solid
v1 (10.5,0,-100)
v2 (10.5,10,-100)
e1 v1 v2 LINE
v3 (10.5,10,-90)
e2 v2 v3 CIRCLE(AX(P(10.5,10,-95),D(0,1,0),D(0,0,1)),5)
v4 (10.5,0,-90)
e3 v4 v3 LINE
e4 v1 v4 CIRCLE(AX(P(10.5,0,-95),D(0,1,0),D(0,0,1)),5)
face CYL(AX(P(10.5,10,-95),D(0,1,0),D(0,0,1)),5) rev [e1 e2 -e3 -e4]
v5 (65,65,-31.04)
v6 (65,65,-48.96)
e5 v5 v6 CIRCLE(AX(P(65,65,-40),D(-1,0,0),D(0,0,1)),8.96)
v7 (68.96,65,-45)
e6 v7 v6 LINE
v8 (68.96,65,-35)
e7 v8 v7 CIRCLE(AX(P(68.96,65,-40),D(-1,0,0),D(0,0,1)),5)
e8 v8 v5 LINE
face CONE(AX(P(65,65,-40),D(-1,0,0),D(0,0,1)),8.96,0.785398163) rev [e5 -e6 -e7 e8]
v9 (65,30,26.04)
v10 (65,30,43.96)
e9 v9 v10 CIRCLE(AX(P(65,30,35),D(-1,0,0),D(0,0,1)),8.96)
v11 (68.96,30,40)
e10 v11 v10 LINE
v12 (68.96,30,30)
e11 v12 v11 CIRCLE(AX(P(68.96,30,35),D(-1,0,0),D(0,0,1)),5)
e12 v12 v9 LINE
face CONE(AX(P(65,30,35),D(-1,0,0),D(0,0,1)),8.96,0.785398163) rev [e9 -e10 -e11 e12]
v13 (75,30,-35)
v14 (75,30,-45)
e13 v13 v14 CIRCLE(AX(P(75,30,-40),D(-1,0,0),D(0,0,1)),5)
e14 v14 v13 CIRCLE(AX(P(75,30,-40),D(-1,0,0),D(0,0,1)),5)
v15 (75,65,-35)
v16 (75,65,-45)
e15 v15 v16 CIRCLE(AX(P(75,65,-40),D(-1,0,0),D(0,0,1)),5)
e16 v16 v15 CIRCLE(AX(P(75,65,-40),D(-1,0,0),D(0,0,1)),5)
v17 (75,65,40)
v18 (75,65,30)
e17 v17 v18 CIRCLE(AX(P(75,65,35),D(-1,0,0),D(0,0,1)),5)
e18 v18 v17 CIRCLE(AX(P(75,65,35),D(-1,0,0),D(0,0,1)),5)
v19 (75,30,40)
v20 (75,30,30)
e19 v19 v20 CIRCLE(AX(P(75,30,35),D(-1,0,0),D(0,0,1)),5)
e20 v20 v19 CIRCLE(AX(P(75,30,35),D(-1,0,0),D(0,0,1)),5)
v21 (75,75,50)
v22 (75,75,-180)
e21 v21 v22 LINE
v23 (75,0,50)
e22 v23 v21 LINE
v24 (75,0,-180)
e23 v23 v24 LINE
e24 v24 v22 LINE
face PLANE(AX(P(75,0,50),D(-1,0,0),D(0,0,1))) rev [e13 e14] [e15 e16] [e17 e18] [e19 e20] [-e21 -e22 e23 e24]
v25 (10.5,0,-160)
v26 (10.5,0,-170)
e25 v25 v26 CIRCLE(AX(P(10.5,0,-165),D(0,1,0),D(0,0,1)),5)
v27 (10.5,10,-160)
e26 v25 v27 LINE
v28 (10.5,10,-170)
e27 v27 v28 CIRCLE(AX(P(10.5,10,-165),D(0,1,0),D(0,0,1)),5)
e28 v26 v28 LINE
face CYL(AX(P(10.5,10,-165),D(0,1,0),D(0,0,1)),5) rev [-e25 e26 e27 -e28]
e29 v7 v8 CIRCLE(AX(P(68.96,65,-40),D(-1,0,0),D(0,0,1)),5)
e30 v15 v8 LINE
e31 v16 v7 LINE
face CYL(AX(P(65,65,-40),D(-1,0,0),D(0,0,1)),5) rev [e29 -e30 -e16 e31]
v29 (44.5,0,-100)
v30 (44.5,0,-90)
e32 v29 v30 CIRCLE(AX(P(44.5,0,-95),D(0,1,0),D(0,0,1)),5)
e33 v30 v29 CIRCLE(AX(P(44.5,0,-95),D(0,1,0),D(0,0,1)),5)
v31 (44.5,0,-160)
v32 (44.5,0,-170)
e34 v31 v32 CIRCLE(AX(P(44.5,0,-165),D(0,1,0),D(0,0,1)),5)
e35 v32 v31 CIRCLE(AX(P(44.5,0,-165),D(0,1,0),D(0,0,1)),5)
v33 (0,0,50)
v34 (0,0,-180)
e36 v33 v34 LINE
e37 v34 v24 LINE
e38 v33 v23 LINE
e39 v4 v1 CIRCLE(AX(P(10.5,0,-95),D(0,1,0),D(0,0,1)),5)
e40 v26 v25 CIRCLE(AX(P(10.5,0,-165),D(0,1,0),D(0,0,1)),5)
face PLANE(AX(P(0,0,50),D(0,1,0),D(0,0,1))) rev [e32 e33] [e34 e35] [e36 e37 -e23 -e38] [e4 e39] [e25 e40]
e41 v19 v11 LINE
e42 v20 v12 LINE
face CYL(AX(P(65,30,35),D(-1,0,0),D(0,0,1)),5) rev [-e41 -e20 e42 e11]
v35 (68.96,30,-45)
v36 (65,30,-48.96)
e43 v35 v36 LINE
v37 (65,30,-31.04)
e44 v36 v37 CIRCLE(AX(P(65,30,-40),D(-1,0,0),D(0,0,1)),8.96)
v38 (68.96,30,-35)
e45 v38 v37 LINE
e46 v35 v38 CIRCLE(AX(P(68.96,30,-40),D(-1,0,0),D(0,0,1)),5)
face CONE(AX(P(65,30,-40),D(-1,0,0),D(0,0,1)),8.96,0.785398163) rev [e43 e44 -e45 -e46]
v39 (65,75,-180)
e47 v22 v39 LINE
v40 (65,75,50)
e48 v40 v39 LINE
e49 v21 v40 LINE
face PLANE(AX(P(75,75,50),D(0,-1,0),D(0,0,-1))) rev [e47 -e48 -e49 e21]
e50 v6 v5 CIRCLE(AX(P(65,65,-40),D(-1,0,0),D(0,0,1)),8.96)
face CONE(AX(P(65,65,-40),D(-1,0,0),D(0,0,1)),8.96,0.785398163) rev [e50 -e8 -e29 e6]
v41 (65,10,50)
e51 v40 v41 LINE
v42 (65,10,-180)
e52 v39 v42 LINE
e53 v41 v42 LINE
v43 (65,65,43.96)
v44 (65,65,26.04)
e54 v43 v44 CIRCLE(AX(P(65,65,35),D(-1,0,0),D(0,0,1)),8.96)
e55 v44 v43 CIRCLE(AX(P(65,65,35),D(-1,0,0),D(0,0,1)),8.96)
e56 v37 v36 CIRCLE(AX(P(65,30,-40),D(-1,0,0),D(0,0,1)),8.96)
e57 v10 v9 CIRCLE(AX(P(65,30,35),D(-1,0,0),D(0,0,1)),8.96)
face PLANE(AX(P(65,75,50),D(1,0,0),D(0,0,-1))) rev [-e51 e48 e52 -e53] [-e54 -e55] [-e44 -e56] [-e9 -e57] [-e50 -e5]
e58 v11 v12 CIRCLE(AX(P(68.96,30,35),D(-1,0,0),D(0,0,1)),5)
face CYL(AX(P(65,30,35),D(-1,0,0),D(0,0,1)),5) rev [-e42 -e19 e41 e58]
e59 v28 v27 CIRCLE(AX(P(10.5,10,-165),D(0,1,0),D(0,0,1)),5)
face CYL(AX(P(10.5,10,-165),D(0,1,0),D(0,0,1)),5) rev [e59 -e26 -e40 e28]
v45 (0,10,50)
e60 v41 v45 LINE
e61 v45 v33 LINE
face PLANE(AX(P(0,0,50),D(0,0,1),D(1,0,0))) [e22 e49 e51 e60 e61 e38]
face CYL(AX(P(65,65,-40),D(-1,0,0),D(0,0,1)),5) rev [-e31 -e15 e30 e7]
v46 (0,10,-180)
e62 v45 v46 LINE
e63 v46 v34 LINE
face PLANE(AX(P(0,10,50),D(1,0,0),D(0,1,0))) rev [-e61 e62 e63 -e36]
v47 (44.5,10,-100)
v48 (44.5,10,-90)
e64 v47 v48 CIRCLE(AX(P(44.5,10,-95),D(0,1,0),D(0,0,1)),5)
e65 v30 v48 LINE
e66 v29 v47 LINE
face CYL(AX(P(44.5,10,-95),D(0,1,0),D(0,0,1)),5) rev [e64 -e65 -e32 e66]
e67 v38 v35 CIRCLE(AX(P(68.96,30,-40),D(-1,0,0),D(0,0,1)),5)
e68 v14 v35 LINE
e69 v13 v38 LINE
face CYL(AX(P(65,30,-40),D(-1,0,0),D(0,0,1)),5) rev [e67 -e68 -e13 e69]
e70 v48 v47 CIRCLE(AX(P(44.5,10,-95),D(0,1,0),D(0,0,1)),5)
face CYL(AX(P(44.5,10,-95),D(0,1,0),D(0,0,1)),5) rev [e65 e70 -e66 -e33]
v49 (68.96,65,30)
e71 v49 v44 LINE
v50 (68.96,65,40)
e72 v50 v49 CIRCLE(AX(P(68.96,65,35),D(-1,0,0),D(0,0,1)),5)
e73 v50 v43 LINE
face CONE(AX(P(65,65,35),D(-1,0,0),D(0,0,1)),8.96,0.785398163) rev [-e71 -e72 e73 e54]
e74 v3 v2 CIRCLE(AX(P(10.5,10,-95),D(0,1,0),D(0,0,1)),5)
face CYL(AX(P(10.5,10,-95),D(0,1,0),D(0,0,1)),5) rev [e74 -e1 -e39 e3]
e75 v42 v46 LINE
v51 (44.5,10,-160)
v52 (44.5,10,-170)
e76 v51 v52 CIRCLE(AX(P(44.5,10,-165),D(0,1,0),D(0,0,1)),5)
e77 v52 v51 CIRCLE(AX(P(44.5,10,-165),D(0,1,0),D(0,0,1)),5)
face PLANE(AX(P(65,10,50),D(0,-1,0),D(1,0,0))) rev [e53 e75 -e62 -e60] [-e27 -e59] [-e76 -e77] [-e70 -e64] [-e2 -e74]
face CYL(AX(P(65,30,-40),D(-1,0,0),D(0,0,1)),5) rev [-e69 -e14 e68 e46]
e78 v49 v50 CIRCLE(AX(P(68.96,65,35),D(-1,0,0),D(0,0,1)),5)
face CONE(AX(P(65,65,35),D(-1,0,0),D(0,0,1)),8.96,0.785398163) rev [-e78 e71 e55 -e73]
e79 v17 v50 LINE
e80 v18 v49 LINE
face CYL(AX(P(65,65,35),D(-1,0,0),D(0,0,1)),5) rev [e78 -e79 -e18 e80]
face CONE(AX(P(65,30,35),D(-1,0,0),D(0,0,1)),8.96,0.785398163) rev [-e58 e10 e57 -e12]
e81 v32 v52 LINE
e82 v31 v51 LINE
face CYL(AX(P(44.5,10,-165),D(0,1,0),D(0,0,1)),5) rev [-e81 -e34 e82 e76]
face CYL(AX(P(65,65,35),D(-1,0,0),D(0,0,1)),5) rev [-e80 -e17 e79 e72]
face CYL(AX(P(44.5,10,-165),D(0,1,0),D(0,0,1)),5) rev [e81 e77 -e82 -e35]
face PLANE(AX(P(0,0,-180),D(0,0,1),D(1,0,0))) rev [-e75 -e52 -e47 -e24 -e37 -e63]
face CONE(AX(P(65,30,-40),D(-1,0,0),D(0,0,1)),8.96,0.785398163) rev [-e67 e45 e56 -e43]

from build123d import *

# Parameters (mm, degrees)
EXTRUDE_1_DEPTH              = 50
HOLE_WIZARD_M8_1_D           = 10
HOLE_WIZARD_M8_1_CSINK_D     = 17.92
HOLE_WIZARD_M8_1_CSINK_ANGLE = 90
MOVE_FACE_1_BY               = 130
HOLE_WIZARD_M8_1_2_D         = 10


with BuildPart() as part:
    # 草图1 → 凸台-拉伸1 (new, symmetric)
    with BuildSketch(Plane.XY):
        Polygon((0, 0), (75, 0), (75, 75), (65, 75), (65, 10), (0, 10), align=None)
    extrude(amount=EXTRUDE_1_DEPTH, both=True)

    # Hole Wizard M8 _1 (through all)
    with Locations(Plane.ZY.offset(-65)):
        with Locations((-40, 65), (35, 65), (-40, 30), (35, 30)):
            CounterSinkHole(HOLE_WIZARD_M8_1_D / 2, HOLE_WIZARD_M8_1_CSINK_D / 2, counter_sink_angle=HOLE_WIZARD_M8_1_CSINK_ANGLE)

    # Move Face 1: a face moved outward by 130.0
    extrude(part.faces().sort_by_distance((37.5, 7.5, -50))[0], amount=MOVE_FACE_1_BY, dir=(0, 0, -1))

    # Hole Wizard M8 _1 2 (through all)
    with Locations(Plane(origin=(0, 10, 0), x_dir=(1, 0, 0), z_dir=(0, 1, 0))):
        with Locations((10.5, 165), (10.5, 95), (44.5, 165), (44.5, 95)):
            Hole(HOLE_WIZARD_M8_1_2_D / 2)


solid = part.part
